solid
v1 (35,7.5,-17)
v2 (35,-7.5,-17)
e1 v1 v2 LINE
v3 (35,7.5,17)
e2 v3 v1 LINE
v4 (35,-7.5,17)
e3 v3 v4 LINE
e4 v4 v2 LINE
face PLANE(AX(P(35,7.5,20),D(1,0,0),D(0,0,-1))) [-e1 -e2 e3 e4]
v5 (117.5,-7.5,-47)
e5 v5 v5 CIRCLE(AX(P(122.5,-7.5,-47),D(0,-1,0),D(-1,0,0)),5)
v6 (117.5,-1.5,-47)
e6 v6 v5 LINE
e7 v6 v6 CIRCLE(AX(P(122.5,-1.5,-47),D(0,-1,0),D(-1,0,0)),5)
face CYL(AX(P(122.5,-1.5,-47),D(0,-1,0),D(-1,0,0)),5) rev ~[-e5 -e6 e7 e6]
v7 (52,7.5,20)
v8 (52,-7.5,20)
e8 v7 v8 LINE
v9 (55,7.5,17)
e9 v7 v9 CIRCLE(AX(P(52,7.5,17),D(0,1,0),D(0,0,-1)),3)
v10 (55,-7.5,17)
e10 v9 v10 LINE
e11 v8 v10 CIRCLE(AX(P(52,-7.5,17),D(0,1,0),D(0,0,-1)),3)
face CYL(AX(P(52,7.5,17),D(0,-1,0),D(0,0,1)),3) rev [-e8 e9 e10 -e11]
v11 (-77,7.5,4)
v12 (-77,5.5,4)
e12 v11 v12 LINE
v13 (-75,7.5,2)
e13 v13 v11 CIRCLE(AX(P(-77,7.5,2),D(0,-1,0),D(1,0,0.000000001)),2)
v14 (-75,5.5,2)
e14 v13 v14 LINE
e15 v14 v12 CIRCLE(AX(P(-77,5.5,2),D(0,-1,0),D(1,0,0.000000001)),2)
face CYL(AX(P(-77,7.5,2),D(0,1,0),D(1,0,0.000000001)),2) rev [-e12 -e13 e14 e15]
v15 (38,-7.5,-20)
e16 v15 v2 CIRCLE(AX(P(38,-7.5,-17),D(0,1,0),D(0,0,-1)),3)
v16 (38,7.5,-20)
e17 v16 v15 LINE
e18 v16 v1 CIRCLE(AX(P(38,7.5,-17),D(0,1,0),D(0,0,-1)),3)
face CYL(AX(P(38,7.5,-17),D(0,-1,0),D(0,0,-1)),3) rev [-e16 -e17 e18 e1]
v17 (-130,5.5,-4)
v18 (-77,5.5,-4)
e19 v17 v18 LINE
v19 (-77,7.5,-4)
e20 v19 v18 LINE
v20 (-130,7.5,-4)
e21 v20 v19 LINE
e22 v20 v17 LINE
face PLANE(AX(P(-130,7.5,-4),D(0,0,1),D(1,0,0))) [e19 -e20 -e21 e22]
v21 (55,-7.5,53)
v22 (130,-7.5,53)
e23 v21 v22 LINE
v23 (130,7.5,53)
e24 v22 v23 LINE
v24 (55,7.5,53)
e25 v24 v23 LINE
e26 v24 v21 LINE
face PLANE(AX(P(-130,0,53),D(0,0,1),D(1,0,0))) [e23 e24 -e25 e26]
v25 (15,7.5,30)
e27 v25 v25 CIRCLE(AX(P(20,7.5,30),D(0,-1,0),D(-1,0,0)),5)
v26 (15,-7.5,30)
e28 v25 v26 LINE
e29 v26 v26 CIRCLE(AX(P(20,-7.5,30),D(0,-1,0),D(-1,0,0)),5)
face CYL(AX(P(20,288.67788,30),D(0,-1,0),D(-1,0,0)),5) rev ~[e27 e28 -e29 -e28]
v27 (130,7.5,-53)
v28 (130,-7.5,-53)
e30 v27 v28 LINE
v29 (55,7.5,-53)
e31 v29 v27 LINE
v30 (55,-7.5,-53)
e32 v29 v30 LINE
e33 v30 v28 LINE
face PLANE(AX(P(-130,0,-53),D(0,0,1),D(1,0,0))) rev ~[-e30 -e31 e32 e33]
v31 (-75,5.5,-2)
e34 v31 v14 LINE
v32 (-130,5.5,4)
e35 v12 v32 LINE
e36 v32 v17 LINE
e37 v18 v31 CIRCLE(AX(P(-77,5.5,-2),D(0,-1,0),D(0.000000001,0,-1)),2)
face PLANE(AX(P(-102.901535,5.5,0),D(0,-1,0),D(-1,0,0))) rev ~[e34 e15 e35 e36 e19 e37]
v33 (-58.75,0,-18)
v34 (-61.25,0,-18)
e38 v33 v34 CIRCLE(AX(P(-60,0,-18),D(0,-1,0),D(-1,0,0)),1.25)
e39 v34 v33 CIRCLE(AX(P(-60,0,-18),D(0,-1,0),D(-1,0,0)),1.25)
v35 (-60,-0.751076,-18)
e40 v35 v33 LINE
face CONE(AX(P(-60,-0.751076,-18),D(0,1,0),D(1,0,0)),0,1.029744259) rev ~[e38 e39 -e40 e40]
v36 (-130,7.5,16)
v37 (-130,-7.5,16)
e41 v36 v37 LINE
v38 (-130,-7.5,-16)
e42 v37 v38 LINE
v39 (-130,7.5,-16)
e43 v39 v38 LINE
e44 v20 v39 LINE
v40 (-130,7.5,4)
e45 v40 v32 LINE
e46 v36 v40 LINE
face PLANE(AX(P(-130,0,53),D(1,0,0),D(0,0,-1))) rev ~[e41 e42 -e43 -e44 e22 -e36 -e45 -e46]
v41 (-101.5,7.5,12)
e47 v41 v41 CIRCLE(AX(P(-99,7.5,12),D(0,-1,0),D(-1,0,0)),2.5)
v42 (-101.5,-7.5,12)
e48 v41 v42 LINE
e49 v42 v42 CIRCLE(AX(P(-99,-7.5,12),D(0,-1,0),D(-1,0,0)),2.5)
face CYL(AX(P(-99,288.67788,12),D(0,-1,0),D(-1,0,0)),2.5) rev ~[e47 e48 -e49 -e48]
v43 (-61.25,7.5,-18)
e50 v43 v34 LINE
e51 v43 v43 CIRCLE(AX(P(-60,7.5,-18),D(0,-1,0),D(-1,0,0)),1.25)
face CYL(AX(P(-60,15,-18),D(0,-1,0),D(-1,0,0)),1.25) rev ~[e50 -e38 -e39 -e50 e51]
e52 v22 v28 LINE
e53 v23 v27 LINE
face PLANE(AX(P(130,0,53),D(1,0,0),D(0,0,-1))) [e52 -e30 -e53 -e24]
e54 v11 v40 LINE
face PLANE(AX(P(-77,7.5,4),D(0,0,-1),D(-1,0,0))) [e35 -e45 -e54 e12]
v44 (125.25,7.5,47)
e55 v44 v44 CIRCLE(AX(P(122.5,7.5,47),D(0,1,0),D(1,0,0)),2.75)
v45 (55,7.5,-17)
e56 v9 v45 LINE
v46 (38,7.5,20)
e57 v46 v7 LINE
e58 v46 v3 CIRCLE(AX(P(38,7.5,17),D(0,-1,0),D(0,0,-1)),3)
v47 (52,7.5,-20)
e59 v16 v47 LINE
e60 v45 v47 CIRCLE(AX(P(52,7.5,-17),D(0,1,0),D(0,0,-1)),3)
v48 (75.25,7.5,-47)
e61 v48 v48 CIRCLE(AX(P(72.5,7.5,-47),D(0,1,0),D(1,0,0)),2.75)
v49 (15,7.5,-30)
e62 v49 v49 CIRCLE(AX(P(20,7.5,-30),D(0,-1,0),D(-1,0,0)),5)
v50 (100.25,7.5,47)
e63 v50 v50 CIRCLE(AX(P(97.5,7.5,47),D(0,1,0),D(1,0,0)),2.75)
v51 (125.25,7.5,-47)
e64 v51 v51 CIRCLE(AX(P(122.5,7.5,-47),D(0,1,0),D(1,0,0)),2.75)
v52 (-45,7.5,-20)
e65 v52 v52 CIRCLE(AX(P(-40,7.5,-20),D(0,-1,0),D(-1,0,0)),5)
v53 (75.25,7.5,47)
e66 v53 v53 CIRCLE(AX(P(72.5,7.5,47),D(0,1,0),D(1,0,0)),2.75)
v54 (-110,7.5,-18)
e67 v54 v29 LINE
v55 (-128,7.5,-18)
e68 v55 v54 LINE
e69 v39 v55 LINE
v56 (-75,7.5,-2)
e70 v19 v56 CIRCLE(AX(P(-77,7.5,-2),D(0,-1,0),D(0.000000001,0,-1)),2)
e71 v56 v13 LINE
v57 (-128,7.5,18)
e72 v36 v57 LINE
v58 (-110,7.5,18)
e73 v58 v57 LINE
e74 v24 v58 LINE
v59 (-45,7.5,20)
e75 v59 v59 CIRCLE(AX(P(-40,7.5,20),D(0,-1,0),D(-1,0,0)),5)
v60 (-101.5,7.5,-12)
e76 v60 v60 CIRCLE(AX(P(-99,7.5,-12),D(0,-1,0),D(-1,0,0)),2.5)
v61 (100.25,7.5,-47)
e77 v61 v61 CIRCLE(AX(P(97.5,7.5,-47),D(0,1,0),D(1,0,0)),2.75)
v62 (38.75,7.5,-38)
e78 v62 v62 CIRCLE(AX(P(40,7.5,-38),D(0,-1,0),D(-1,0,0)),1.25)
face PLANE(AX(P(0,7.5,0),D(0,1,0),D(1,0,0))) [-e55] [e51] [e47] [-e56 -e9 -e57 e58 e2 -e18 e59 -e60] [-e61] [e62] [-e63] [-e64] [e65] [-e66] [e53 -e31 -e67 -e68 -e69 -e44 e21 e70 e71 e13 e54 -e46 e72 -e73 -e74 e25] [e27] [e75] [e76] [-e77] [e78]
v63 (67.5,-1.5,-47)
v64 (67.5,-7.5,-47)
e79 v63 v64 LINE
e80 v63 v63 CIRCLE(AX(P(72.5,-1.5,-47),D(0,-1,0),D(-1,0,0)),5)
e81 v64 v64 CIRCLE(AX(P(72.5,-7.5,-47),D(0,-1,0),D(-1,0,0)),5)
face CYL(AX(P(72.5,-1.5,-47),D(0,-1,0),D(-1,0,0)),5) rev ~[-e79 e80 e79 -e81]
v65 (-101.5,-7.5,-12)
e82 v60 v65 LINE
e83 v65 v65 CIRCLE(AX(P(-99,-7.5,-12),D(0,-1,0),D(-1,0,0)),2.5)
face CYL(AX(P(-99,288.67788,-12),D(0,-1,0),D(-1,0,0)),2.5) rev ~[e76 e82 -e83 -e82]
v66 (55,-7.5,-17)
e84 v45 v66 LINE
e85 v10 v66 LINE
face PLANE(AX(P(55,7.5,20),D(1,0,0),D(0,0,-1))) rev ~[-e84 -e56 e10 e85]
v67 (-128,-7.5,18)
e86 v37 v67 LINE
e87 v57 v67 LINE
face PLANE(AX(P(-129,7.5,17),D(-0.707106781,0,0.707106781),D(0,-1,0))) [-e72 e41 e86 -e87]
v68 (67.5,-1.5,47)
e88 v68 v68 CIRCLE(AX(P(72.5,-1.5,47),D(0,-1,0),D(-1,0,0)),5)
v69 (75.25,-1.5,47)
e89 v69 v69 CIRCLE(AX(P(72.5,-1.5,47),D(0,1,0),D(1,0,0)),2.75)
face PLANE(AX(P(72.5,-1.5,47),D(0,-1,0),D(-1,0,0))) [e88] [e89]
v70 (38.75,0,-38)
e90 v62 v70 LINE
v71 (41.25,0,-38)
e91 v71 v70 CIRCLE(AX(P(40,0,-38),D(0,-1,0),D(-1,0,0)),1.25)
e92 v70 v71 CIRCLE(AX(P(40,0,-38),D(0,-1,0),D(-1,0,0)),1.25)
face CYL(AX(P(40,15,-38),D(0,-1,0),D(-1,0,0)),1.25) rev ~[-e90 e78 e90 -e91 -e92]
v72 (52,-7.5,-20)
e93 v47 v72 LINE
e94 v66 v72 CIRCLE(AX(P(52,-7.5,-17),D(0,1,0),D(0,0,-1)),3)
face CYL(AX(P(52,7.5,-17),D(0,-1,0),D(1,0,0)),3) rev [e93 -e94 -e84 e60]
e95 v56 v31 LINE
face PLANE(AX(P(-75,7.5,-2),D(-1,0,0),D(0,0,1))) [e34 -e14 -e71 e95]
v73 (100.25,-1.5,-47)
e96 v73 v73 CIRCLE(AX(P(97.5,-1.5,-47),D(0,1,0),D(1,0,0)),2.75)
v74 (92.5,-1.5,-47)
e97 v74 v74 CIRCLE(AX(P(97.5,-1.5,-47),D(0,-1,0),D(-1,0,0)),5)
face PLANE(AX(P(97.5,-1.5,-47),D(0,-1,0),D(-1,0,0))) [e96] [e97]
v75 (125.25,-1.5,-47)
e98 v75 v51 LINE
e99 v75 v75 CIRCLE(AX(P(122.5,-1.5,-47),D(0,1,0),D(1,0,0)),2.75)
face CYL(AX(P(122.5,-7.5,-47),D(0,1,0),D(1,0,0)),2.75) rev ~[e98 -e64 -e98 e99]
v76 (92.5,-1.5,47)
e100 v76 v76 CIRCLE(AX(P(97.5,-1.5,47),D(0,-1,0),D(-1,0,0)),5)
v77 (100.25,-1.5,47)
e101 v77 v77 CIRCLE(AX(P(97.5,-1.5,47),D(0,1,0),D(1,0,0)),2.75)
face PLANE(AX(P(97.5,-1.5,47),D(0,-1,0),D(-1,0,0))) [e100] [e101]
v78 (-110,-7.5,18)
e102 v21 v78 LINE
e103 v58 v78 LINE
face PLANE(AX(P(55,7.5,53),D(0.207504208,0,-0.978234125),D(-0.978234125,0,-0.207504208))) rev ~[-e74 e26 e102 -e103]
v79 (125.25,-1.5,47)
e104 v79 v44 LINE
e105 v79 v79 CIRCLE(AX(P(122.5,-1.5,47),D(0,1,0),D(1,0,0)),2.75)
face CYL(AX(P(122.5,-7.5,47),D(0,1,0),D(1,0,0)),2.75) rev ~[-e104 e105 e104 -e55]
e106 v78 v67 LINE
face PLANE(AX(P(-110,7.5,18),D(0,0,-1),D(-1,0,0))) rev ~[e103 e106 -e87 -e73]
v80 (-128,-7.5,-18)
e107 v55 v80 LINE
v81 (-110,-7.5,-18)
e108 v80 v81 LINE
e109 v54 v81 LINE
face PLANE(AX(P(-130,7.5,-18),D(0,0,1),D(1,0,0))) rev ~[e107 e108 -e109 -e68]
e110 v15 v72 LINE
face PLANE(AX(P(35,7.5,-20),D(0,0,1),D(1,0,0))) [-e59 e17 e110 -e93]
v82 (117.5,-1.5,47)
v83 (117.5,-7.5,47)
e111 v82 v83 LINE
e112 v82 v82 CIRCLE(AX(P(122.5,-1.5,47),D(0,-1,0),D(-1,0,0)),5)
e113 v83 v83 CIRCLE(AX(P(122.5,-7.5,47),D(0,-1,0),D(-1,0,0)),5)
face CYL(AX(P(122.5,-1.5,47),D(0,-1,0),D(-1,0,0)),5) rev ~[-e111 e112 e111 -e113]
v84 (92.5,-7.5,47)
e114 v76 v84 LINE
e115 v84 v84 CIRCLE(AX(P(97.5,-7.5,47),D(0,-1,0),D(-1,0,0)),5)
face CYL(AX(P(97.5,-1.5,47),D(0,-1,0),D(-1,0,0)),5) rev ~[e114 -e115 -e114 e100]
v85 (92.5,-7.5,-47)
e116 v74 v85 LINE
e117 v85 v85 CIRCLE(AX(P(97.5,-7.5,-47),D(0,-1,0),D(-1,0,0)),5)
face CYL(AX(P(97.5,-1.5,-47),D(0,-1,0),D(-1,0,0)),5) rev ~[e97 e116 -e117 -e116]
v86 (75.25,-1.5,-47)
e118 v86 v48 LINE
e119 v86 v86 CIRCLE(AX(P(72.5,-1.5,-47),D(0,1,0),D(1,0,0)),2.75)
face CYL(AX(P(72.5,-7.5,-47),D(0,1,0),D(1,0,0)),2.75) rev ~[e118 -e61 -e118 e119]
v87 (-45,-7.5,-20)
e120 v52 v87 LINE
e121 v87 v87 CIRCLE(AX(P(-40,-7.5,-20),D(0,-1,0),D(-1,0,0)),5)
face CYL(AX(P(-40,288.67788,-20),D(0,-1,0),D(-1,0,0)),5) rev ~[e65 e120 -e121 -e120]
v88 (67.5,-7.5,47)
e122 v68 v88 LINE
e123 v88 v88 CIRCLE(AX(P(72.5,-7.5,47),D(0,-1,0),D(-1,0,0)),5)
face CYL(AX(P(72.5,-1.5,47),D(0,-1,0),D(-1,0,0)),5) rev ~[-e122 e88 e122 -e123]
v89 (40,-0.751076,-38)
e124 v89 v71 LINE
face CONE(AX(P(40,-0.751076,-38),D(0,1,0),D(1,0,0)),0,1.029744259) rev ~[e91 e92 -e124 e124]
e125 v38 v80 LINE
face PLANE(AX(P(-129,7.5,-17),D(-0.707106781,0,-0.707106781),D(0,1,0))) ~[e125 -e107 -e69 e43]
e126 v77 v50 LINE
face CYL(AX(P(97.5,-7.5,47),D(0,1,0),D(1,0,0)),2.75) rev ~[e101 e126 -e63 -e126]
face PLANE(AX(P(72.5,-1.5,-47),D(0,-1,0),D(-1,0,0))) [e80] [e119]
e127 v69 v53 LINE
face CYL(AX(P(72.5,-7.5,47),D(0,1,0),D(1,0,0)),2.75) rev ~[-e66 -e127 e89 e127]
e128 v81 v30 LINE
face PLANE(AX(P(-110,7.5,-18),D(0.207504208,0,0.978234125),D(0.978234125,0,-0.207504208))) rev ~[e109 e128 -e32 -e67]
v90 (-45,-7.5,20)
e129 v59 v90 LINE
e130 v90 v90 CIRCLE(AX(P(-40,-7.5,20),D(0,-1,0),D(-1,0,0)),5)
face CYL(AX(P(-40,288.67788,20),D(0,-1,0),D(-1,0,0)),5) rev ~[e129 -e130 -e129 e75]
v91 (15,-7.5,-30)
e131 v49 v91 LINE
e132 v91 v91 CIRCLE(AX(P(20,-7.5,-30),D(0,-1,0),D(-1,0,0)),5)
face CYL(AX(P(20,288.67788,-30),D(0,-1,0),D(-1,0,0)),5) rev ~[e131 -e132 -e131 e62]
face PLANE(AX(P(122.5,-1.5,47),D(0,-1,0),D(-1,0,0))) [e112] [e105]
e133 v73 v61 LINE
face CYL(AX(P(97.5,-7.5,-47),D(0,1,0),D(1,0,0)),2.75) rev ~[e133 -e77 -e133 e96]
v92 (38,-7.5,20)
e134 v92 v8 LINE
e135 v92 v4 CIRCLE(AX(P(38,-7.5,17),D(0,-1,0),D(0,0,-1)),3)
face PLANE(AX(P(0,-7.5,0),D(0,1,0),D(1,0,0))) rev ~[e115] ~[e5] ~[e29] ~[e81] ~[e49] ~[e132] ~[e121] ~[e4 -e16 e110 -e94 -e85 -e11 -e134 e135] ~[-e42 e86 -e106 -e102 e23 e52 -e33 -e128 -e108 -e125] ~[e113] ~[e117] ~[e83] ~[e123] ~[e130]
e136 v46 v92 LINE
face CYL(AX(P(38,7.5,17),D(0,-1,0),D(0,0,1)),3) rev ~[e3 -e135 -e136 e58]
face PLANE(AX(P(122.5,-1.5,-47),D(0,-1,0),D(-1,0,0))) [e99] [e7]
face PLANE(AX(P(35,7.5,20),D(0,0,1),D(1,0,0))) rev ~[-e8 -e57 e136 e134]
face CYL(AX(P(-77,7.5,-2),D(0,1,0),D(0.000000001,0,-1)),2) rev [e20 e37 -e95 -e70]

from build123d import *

# Parameters (mm, degrees)
SKETCH1_W                                            = 260
SKETCH1_H                                            = 106
BOSS_EXTRUDE1_DEPTH                                  = 7.5
CUT_EXTRUDE1_DEPTH                                   = 142.187818171
CUT_EXTRUDE2_DEPTH                                   = 2
M6_TAPPED_HOLE1_D                                    = 5
SKETCH9_W                                            = 20
SKETCH9_H                                            = 40
CUT_EXTRUDE4_DEPTH                                   = 142.187818171
FILLET5_R                                            = 3
HOLE_SIZE_PER_SOCKET_HEAD_CAP_SCREW_TYPE_D           = 5.5
HOLE_SIZE_PER_SOCKET_HEAD_CAP_SCREW_TYPE_CBORE_D     = 10
HOLE_SIZE_PER_SOCKET_HEAD_CAP_SCREW_TYPE_CBORE_DEPTH = 6
CHAMFER1_SIZE                                        = 2
M3_TAPPED_HOLE1_D                                    = 2.5
M3_TAPPED_HOLE1_DEPTH                                = 7.5
M3_TAPPED_HOLE1_TIP                                  = 0.751075774
F_10_0_10_DIAMETER_HOLE1_D                           = 10


with BuildPart() as part:
    # Sketch1 → Boss-Extrude1 (new, symmetric)
    with BuildSketch(Plane(origin=(0, 0, 0), x_dir=(1, 0, 0), z_dir=(0, 1, 0))):
        Rectangle(SKETCH1_W, SKETCH1_H)
    extrude(amount=BOSS_EXTRUDE1_DEPTH, both=True)

    # Sketch2 → Cut-Extrude1 (cut, through all)
    with BuildSketch(Plane(origin=(0, 7.5, 0), x_dir=(1, 0, 0), z_dir=(0, 1, 0))):
        Polygon((55, 53), (-130, 53), (-130, 18), (-110, 18), align=None)
        Polygon((-130, -18), (-130, -53), (55, -53), (-110, -18), align=None)
    extrude(amount=-CUT_EXTRUDE1_DEPTH, mode=Mode.SUBTRACT)

    # Sketch3 → Cut-Extrude2 (cut)
    with BuildSketch(Plane(origin=(0, 7.5, 0), x_dir=(1, 0, 0), z_dir=(0, 1, 0))):
        with BuildLine():
            Line((-130, 4), (-77, 4))
            ThreePointArc((-77, 4), (-75.585786438, 3.414213562), (-75, 2))
            Line((-75, 2), (-75, -2))
            ThreePointArc((-75, -2), (-75.585786438, -3.414213562), (-77, -4))
            Line((-77, -4), (-130, -4))
            Line((-130, -4), (-130, 4))
        make_face()
    extrude(amount=-CUT_EXTRUDE2_DEPTH, mode=Mode.SUBTRACT)

    # M6 Tapped Hole1 (through all)
    with Locations(Plane(origin=(0, 7.5, 0), x_dir=(1, 0, 0), z_dir=(0, 1, 0))):
        with Locations((-99, 12), (-99, -12)):
            Hole(M6_TAPPED_HOLE1_D / 2)

    # Sketch9 → Cut-Extrude4 (cut, through all)
    with BuildSketch(Plane(origin=(0, 7.5, 0), x_dir=(1, 0, 0), z_dir=(0, 1, 0))):
        with Locations((45, 0)):
            Rectangle(SKETCH9_W, SKETCH9_H)
    extrude(amount=-CUT_EXTRUDE4_DEPTH, mode=Mode.SUBTRACT)

    # Fillet5
    fillet5_edges = [part.edges().sort_by_distance(p)[0] for p in [
        (55, 0, -20),
        (55, 0, 20),
        (35, 0, 20),
        (35, 0, -20),
    ]]
    fillet(fillet5_edges, radius=FILLET5_R)

    # Hole size per socket head cap screw type1 (through all)
    with Locations(Plane(origin=(0, -7.5, 0), x_dir=(-1, 0, 0), z_dir=(0, -1, 0))):
        with Locations((-122.5, -47), (-97.5, -47), (-72.5, -47), (-72.5, 47), (-97.5, 47), (-122.5, 47)):
            CounterBoreHole(HOLE_SIZE_PER_SOCKET_HEAD_CAP_SCREW_TYPE_D / 2, HOLE_SIZE_PER_SOCKET_HEAD_CAP_SCREW_TYPE_CBORE_D / 2, HOLE_SIZE_PER_SOCKET_HEAD_CAP_SCREW_TYPE_CBORE_DEPTH)

    # Chamfer1
    chamfer1_edges = [part.edges().sort_by_distance(p)[0] for p in [
        (-130, 0, -18),
        (-130, 0, 18),
    ]]
    chamfer(chamfer1_edges, length=CHAMFER1_SIZE)

    # M3 Tapped Hole1
    with Locations(Plane(origin=(0, 7.5, 0), x_dir=(1, 0, 0), z_dir=(0, 1, 0))):
        with Locations((40, 38), (-60, 18)):
            Hole(M3_TAPPED_HOLE1_D / 2, depth=M3_TAPPED_HOLE1_DEPTH)
            with Locations((0, 0, -(M3_TAPPED_HOLE1_DEPTH + M3_TAPPED_HOLE1_TIP / 2))):  # 118° drill point
                Cone(0, M3_TAPPED_HOLE1_D / 2, M3_TAPPED_HOLE1_TIP, mode=Mode.SUBTRACT)

    # Ø10.0 (10) Diameter Hole1 (through all)
    with Locations(Plane(origin=(0, 7.5, 0), x_dir=(1, 0, 0), z_dir=(0, 1, 0))):
        with Locations((-40, 20), (-40, -20), (20, -30), (20, 30)):
            Hole(F_10_0_10_DIAMETER_HOLE1_D / 2)


solid = part.part
